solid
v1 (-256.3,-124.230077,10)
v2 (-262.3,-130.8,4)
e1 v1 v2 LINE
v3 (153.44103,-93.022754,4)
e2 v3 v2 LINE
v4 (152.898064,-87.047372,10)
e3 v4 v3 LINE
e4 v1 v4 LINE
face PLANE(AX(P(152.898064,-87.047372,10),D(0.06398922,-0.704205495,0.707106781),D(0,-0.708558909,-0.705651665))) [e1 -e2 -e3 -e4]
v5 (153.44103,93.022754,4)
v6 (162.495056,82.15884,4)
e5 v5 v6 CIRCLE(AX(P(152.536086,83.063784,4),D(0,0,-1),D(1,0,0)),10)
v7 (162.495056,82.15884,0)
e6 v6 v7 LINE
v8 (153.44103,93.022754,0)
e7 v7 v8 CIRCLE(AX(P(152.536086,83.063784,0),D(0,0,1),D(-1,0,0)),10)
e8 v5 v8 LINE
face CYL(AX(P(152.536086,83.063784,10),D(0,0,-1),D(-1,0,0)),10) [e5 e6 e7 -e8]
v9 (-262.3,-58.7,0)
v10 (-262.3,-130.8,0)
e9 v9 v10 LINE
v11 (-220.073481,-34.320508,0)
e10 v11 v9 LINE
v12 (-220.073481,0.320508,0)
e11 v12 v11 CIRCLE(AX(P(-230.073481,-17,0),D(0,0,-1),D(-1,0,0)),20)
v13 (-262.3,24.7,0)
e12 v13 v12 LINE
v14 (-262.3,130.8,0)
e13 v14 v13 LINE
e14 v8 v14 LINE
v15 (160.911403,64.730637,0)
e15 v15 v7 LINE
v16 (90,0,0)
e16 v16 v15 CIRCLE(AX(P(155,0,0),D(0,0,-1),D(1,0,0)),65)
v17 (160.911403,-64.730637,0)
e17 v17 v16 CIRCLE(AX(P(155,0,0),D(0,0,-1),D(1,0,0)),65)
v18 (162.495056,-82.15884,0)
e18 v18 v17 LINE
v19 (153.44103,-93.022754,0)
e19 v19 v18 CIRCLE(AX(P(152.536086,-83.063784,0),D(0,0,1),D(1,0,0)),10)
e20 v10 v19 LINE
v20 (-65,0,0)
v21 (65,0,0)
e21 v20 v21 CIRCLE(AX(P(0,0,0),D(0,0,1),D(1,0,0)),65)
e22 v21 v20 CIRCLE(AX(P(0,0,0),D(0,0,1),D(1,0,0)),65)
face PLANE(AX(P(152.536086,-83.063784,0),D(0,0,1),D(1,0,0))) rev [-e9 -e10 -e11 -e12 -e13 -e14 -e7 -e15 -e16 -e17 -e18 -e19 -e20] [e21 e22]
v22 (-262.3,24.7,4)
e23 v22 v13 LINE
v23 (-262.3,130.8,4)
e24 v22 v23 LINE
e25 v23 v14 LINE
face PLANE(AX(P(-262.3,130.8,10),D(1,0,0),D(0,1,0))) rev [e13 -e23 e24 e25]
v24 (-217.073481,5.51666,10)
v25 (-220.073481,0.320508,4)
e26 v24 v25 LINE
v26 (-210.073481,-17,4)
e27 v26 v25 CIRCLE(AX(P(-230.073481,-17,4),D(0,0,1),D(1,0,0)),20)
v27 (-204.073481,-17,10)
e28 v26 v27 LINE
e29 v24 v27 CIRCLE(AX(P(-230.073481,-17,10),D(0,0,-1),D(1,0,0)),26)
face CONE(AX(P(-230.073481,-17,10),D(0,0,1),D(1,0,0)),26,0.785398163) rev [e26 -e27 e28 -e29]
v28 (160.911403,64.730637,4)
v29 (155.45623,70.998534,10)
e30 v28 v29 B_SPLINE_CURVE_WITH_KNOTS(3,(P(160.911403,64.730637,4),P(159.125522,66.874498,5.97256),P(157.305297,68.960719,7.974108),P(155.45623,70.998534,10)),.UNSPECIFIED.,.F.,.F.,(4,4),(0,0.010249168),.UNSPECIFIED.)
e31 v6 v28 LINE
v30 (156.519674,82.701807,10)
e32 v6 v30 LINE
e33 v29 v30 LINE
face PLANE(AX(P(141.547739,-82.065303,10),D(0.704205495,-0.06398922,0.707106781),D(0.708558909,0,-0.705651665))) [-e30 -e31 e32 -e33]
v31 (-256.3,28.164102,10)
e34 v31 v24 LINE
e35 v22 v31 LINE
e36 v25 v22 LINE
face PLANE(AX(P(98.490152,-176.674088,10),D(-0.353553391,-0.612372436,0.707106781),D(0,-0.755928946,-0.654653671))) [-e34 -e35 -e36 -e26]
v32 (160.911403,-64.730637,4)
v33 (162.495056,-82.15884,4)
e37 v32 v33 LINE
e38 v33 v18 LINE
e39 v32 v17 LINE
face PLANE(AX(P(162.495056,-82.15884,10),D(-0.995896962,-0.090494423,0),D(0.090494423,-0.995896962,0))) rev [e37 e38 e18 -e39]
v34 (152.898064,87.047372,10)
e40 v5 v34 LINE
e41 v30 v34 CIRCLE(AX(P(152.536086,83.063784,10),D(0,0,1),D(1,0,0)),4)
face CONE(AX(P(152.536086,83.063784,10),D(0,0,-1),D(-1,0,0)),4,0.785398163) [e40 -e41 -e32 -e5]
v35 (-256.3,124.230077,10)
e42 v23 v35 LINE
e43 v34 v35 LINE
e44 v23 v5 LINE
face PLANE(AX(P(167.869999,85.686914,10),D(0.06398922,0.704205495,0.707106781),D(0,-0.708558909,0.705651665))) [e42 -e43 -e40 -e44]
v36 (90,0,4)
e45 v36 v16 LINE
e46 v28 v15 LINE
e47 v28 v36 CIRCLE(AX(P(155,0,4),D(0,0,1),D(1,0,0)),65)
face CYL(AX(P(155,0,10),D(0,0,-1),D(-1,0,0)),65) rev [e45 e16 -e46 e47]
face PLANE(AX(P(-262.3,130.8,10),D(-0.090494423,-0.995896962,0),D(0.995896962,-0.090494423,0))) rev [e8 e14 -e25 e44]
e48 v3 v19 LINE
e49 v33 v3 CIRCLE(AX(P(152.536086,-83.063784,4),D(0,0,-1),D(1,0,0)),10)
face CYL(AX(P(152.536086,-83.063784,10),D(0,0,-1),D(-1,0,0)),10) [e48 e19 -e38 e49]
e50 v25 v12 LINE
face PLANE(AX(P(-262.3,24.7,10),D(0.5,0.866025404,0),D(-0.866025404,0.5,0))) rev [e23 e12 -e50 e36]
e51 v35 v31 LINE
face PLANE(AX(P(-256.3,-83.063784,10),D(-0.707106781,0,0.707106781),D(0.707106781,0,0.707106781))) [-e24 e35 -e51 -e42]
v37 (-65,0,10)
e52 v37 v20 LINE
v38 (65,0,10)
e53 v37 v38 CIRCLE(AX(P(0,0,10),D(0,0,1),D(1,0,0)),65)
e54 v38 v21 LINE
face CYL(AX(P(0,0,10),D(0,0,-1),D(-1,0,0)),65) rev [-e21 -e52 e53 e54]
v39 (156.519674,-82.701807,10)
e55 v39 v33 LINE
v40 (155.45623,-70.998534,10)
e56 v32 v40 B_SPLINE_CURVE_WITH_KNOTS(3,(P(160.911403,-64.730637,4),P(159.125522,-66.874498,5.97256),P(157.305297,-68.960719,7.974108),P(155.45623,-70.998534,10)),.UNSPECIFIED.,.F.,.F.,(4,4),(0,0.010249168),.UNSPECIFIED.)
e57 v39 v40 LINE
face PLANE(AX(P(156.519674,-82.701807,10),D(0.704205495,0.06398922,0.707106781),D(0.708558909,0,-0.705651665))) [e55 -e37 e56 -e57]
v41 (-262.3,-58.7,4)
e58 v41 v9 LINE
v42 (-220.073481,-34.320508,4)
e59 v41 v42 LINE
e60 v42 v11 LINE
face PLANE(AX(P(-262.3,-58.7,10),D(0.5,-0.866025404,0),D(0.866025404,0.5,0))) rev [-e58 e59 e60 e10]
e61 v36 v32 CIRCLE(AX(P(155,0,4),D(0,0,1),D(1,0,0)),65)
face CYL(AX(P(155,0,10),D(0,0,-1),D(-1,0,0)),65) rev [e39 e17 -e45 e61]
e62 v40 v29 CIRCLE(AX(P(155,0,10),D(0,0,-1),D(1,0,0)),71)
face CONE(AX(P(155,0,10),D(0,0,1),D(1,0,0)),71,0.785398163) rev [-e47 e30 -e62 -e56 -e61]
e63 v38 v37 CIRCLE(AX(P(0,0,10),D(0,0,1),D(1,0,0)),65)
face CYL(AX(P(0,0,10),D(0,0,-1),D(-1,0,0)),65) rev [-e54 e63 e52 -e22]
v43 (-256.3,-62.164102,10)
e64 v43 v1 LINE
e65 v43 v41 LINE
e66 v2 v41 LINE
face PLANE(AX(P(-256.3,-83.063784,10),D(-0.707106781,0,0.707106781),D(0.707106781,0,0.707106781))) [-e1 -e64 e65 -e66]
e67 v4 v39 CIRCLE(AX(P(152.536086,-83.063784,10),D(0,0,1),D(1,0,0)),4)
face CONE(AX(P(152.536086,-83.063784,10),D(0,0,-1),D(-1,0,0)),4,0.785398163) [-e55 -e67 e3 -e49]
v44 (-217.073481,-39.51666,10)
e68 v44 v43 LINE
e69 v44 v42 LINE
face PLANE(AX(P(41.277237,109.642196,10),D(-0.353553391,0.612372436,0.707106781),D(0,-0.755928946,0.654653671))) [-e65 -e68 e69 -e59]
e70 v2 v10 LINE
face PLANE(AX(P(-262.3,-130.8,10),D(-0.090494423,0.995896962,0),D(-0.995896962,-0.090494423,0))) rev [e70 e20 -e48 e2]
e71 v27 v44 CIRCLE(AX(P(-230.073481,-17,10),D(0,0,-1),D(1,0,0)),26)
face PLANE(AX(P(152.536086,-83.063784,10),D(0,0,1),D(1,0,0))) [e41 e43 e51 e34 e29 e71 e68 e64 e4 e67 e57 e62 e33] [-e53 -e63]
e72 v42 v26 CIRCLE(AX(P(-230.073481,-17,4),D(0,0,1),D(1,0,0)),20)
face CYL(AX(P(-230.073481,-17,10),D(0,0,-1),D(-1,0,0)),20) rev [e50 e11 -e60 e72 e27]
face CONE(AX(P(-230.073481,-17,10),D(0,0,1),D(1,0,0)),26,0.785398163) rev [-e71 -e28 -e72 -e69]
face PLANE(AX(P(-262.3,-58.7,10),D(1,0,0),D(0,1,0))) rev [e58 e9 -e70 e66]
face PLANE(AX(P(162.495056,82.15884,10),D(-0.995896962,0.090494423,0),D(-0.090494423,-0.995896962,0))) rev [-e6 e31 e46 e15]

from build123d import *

# Parameters (mm, degrees)
SKETCH1_R           = 65
BOSS_EXTRUDE1_DEPTH = 10
CHAMFER1_SIZE       = 6


with BuildPart() as part:
    # Sketch1 → Boss-Extrude1 (new body)
    with BuildSketch(Plane.XY):
        with BuildLine():
            Line((-262.3, 130.8), (-262.3, 24.7))
            Line((-262.3, 24.7), (-220.073481324, 0.320508076))
            ThreePointArc((-220.073481324, 0.320508076), (-210.073481324, -17), (-220.073481324, -34.320508076))
            Line((-220.073481324, -34.320508076), (-262.3, -58.7))
            Line((-262.3, -58.7), (-262.3, -130.8))
            Line((-262.3, -130.8), (153.441030377, -93.022753927))
            ThreePointArc((153.441030377, -93.022753927), (160.218033303, -89.465947057), (162.495055771, -82.158840075))
            Line((162.495055771, -82.158840075), (160.91140277, -64.73063662))
            ThreePointArc((160.91140277, -64.73063662), (90, 0), (160.91140277, 64.73063662))
            Line((160.91140277, 64.73063662), (162.495055771, 82.158840075))
            ThreePointArc((162.495055771, 82.158840075), (160.218033303, 89.465947057), (153.441030377, 93.022753927))
            Line((153.441030377, 93.022753927), (-262.3, 130.8))
        make_face()
        Circle(SKETCH1_R, mode=Mode.SUBTRACT)
    extrude(amount=BOSS_EXTRUDE1_DEPTH)

    # Chamfer1
    chamfer1_edges = [part.edges().sort_by_distance(p)[0] for p in [
        (160.218033303, -89.465947057, 10),
        (161.703229271, -73.444738348, 10),
        (90, 0, 10),
        (161.703229271, 73.444738348, 10),
        (160.218033303, 89.465947057, 10),
        (-54.429484811, 111.911376963, 10),
        (-262.3, 77.75, 10),
        (-241.186740662, 12.510254038, 10),
        (-210.073481324, -17, 10),
        (-241.186740662, -46.510254038, 10),
        (-262.3, -94.75, 10),
        (-54.429484811, -111.911376963, 10),
    ]]
    chamfer(chamfer1_edges, length=CHAMFER1_SIZE)


solid = part.part
